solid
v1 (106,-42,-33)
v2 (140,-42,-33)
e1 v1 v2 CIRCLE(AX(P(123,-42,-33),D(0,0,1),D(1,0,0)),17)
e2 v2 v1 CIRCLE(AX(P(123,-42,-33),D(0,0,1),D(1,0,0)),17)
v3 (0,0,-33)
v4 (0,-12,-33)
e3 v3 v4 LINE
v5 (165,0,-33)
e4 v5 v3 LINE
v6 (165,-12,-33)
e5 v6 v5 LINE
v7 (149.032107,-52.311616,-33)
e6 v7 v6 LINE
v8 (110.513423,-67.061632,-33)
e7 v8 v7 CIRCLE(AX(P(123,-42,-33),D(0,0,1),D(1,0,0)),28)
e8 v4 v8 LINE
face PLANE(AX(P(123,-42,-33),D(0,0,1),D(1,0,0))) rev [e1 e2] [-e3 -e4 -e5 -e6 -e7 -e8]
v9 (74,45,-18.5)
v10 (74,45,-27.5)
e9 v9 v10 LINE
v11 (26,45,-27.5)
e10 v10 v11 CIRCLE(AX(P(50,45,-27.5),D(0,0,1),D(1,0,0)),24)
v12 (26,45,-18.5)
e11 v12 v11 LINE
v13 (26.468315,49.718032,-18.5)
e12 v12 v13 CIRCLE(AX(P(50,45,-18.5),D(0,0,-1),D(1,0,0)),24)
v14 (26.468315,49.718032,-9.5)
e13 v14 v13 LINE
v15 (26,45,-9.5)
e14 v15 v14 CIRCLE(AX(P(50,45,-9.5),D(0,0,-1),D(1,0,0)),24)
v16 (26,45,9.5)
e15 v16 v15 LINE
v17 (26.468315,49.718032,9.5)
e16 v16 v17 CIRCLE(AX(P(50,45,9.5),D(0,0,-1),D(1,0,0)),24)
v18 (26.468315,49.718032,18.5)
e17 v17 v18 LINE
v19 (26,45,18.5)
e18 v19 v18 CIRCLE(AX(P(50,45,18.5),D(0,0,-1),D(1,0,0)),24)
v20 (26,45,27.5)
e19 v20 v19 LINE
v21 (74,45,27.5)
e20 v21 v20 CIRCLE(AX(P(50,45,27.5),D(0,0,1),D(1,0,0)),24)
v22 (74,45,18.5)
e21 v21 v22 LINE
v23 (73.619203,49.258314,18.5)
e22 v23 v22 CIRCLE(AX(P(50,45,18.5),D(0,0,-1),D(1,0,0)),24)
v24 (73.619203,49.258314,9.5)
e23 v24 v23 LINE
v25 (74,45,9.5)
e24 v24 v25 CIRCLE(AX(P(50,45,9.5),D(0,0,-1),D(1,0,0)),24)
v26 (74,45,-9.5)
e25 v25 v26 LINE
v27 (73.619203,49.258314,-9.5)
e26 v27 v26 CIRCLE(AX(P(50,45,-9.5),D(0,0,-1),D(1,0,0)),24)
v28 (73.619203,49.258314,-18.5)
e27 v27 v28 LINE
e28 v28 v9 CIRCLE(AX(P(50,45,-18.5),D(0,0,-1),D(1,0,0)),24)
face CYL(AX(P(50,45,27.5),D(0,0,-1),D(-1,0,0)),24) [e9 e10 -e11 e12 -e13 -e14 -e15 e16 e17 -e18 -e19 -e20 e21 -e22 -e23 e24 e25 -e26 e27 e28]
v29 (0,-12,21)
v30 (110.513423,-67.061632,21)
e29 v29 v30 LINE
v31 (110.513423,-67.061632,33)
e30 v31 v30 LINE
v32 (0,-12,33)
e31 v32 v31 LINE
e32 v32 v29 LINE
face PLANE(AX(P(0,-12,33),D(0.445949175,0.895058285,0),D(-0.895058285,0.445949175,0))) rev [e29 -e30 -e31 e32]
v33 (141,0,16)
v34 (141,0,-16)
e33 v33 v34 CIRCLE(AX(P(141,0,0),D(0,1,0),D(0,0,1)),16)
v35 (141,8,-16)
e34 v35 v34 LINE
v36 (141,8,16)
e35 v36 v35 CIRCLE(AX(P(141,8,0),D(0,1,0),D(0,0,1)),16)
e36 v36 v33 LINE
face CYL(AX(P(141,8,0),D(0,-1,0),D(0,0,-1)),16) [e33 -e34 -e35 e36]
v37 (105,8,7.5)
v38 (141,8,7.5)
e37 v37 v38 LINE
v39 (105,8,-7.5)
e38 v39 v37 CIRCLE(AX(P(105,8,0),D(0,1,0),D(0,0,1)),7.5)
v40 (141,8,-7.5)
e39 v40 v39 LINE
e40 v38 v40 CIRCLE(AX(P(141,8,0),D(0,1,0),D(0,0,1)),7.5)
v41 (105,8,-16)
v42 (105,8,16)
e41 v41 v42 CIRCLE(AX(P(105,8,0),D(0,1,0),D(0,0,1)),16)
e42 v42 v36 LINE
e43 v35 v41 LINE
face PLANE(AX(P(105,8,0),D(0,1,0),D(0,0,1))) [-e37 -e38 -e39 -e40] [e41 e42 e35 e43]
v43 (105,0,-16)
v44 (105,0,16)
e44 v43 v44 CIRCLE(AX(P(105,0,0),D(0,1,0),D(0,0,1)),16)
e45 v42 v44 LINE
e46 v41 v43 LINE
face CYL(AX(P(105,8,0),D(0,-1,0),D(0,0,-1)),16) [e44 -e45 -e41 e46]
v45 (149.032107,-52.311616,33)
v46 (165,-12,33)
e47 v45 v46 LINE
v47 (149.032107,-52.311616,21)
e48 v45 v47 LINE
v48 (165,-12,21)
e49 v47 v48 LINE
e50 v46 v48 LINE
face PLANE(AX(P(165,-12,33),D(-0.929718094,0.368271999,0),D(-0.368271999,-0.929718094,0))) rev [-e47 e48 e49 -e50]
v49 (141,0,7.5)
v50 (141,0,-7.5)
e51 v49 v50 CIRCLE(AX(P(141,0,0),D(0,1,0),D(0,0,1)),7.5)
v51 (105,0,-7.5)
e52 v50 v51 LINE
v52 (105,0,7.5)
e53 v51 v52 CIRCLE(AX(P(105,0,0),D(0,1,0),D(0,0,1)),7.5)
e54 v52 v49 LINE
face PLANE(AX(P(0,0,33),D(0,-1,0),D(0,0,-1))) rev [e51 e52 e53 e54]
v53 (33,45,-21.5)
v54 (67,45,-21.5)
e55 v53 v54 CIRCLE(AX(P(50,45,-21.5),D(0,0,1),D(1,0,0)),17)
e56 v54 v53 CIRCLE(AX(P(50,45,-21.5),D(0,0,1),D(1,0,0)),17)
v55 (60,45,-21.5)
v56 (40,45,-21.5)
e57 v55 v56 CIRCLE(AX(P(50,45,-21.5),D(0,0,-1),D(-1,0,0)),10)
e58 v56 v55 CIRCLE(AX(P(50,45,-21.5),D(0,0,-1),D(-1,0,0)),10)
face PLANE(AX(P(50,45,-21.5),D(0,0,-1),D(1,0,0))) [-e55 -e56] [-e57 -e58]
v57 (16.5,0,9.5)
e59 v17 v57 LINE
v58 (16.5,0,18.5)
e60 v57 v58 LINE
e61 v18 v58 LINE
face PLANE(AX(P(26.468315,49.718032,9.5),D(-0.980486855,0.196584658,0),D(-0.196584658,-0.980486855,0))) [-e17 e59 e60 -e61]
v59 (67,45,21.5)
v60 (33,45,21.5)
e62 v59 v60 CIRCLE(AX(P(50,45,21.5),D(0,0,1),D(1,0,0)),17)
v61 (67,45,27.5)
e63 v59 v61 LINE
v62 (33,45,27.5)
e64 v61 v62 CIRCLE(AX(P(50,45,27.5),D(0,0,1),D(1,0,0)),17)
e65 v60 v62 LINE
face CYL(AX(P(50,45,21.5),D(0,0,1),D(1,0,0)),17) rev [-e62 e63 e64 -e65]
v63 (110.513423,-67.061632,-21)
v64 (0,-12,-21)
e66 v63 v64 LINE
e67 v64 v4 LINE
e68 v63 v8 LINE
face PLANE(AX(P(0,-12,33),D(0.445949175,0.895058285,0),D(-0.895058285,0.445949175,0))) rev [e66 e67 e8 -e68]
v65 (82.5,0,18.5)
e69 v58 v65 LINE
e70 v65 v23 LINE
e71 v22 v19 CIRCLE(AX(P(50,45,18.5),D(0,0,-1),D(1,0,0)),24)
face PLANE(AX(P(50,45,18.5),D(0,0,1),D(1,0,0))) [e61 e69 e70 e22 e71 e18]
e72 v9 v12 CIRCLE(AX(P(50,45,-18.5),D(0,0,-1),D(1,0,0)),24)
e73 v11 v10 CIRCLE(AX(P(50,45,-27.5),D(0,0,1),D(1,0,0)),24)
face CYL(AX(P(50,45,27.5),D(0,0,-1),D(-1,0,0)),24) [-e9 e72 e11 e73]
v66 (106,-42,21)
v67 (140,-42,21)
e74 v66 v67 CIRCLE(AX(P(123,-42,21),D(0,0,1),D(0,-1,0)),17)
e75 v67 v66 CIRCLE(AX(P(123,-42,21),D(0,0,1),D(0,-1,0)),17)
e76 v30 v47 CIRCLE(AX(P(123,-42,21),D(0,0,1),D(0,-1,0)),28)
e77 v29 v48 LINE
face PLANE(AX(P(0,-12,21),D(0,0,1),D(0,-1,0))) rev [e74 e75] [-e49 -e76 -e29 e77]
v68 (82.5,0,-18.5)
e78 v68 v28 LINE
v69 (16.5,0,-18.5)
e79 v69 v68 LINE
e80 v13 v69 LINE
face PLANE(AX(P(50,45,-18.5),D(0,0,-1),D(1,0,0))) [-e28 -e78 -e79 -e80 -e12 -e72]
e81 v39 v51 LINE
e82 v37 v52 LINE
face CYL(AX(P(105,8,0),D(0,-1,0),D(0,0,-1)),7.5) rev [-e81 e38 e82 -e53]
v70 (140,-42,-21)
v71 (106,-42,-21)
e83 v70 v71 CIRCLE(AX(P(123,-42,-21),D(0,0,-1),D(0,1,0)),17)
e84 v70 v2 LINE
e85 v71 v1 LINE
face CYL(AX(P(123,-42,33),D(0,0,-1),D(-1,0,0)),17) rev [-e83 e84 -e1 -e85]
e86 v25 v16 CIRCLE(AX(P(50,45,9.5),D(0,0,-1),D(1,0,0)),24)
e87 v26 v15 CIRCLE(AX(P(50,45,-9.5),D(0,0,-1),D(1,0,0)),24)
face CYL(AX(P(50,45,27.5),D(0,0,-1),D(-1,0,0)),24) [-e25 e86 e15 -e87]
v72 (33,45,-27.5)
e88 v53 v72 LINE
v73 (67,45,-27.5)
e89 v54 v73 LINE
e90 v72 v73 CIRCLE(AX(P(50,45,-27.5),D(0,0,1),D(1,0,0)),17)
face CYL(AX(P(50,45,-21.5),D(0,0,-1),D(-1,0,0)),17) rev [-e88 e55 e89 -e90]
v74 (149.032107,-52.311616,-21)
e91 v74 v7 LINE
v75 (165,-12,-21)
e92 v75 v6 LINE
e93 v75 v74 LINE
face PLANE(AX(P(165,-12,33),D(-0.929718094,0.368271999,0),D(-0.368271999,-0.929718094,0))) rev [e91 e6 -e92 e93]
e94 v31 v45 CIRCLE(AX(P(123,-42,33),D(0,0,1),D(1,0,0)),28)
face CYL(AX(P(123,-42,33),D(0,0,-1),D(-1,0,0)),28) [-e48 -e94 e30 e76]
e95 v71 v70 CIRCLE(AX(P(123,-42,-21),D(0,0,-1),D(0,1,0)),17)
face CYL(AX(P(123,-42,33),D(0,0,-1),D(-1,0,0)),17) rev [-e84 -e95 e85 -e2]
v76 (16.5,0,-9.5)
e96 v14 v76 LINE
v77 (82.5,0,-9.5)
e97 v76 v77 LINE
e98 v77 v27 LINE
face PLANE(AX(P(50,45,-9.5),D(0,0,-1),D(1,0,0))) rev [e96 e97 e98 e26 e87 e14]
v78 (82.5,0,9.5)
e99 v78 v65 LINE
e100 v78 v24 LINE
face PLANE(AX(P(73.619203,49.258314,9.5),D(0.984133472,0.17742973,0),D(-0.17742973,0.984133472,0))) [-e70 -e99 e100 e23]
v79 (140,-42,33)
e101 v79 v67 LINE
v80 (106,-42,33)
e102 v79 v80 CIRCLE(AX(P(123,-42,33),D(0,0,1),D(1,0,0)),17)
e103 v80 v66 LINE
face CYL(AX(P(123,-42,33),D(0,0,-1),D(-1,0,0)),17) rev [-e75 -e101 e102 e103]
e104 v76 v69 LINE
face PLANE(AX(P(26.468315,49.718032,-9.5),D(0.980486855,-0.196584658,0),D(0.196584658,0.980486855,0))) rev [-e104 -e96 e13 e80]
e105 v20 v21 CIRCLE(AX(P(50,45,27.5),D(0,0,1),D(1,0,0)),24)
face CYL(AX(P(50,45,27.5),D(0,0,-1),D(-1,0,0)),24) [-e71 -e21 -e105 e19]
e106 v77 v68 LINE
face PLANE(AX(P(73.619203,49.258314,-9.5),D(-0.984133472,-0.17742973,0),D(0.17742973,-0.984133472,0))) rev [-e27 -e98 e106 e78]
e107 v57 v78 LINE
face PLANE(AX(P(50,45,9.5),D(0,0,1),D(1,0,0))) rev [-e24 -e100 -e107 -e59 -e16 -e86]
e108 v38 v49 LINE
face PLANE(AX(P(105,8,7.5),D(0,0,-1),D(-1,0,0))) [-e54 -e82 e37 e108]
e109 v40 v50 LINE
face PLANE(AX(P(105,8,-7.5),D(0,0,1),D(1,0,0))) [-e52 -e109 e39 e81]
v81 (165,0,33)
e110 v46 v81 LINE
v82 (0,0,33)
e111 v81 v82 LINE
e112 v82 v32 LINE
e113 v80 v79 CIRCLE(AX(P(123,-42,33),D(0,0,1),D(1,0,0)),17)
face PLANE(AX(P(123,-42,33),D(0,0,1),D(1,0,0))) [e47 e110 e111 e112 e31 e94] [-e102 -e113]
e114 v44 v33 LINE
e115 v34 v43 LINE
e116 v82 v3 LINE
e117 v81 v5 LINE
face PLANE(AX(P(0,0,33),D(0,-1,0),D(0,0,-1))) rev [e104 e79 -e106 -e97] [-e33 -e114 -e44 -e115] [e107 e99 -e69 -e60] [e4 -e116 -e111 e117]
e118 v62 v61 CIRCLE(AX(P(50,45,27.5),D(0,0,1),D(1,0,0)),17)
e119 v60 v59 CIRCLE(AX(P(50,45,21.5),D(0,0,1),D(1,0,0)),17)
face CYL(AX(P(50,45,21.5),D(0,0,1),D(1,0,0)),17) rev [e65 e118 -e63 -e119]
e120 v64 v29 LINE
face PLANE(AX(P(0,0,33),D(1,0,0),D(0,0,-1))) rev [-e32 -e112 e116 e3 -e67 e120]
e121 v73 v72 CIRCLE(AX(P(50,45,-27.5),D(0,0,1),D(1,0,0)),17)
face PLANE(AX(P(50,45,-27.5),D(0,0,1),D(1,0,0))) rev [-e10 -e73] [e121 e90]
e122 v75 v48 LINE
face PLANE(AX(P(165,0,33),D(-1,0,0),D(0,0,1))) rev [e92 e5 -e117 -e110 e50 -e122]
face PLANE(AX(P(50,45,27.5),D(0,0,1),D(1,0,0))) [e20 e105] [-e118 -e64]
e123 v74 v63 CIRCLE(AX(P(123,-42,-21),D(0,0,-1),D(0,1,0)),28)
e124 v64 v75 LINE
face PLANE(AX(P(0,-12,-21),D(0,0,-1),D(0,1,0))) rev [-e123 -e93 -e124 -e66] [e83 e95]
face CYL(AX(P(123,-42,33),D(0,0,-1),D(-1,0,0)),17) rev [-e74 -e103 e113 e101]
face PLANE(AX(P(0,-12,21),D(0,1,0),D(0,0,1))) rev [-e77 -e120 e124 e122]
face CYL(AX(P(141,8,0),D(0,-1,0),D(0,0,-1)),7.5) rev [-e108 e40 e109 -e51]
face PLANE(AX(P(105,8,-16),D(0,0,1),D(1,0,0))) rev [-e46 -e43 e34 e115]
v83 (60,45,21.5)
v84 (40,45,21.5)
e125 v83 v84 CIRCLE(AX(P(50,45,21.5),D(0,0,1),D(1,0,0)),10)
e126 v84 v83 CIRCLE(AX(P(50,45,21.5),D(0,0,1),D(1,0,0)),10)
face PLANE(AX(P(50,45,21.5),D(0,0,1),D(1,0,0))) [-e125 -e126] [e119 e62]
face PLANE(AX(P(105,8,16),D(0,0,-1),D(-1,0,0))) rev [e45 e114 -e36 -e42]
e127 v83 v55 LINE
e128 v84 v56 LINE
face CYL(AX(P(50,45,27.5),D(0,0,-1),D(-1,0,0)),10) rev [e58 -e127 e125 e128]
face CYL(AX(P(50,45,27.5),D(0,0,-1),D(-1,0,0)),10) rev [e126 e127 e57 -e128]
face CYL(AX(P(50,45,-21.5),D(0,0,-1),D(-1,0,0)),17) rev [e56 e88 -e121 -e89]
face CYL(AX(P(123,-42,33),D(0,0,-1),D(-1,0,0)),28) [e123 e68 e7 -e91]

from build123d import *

# Parameters (mm, degrees)
STANCHION_PROFILE_SKETCH_R = 17
STANCHION_BODY_DEPTH       = 33
CORNER_NOTCH_SKETCH_W      = 42
CORNER_NOTCH_SKETCH_H      = 58
CORNER_NOTCH_12X12_DEPTH   = 183.247085025
SLOTTED_BOSS_DEPTH         = 8
HINGE_BARREL_SKETCH_R      = 24
HINGE_BARREL_SKETCH_R_2    = 10
HINGE_BARREL_DEPTH         = 27.5
BARREL_START               = -9
BARREL_GUSSET_DEPTH        = 9
BARREL_RECESS_SKETCH_R     = 17
BARREL_RECESS_CUT_DEPTH    = 6


with BuildPart() as part:
    # Stanchion Profile Sketch → Stanchion Body (new, symmetric)
    with BuildSketch(Plane.XY):
        with BuildLine():
            Line((0, 0), (165, 0))
            Line((165, 0), (165, -12))
            Line((165, -12), (149.032106642, -52.311615965))
            ThreePointArc((149.032106642, -52.311615965), (133.013045842, -68.148401729), (110.513423096, -67.061631974))
            Line((110.513423096, -67.061631974), (0, -12))
            Line((0, -12), (0, 0))
        make_face()
        with Locations((123, -42)):
            Circle(STANCHION_PROFILE_SKETCH_R, mode=Mode.SUBTRACT)
    extrude(amount=STANCHION_BODY_DEPTH, both=True)

    # Corner Notch Sketch → Corner Notch 12x12 (cut, through all)
    with BuildSketch(Plane(origin=(165, 0, 0), x_dir=(0, 0, -1), z_dir=(1, 0, 0))):
        with Locations((0, -41)):
            Rectangle(CORNER_NOTCH_SKETCH_W, CORNER_NOTCH_SKETCH_H)
    extrude(amount=-CORNER_NOTCH_12X12_DEPTH, mode=Mode.SUBTRACT)

    # Slotted Boss Sketch → Slotted Boss (add)
    with BuildSketch(Plane(origin=(0, 0, 0), x_dir=(1, 0, 0), z_dir=(0, 1, 0))):
        with BuildLine():
            Line((105, 16), (141, 16))
            ThreePointArc((141, 16), (157, 0), (141, -16))
            Line((141, -16), (105, -16))
            ThreePointArc((105, -16), (89, 0), (105, 16))
        make_face()
        with BuildLine():
            Line((105, 7.5), (141, 7.5))
            ThreePointArc((141, 7.5), (148.5, 0), (141, -7.5))
            Line((141, -7.5), (105, -7.5))
            ThreePointArc((105, -7.5), (97.5, 0), (105, 7.5))
        make_face(mode=Mode.SUBTRACT)
    extrude(amount=SLOTTED_BOSS_DEPTH)



with BuildPart() as body_2:
    # Hinge Barrel Sketch → Hinge Barrel (new, symmetric)
    with BuildSketch(Plane.XY):
        with Locations((50, 45)):
            Circle(HINGE_BARREL_SKETCH_R)
        with Locations((50, 45)):
            Circle(HINGE_BARREL_SKETCH_R_2, mode=Mode.SUBTRACT)
    extrude(amount=HINGE_BARREL_DEPTH, both=True)


with BuildPart() as part_1:
    add(part.part)

    add(body_2.part)  # Barrel Gusset merges body 2
    # Barrel Gusset Sketch → Barrel Gusset (add)
    with BuildSketch(Plane.XY.offset(27.5).offset(BARREL_START)):
        with BuildLine():
            Line((73.619203331, 49.258313517), (82.5, 0))
            Line((82.5, 0), (16.5, 0))
            Line((16.5, 0), (26.468315489, 49.718031802))
            ThreePointArc((26.468315489, 49.718031802), (49.766012583, 21.001140654), (73.619203331, 49.258313517))
        make_face()
    barrel_gusset = extrude(amount=-BARREL_GUSSET_DEPTH)

    # Barrel Gusset Mirror: Barrel Gusset across plane
    add(barrel_gusset.mirror(Plane.XY))

    # Barrel Recess Sketch → Barrel Recess Cut (cut)
    with BuildSketch(Plane.XY.offset(27.5)):
        with Locations((50, 45)):
            Circle(BARREL_RECESS_SKETCH_R)
    barrel_recess_cut = extrude(amount=-BARREL_RECESS_CUT_DEPTH, mode=Mode.SUBTRACT)

    # Barrel Recess Mirror: Barrel Recess Cut across plane
    add(barrel_recess_cut.mirror(Plane.XY), mode=Mode.SUBTRACT)


solid = part_1.part
